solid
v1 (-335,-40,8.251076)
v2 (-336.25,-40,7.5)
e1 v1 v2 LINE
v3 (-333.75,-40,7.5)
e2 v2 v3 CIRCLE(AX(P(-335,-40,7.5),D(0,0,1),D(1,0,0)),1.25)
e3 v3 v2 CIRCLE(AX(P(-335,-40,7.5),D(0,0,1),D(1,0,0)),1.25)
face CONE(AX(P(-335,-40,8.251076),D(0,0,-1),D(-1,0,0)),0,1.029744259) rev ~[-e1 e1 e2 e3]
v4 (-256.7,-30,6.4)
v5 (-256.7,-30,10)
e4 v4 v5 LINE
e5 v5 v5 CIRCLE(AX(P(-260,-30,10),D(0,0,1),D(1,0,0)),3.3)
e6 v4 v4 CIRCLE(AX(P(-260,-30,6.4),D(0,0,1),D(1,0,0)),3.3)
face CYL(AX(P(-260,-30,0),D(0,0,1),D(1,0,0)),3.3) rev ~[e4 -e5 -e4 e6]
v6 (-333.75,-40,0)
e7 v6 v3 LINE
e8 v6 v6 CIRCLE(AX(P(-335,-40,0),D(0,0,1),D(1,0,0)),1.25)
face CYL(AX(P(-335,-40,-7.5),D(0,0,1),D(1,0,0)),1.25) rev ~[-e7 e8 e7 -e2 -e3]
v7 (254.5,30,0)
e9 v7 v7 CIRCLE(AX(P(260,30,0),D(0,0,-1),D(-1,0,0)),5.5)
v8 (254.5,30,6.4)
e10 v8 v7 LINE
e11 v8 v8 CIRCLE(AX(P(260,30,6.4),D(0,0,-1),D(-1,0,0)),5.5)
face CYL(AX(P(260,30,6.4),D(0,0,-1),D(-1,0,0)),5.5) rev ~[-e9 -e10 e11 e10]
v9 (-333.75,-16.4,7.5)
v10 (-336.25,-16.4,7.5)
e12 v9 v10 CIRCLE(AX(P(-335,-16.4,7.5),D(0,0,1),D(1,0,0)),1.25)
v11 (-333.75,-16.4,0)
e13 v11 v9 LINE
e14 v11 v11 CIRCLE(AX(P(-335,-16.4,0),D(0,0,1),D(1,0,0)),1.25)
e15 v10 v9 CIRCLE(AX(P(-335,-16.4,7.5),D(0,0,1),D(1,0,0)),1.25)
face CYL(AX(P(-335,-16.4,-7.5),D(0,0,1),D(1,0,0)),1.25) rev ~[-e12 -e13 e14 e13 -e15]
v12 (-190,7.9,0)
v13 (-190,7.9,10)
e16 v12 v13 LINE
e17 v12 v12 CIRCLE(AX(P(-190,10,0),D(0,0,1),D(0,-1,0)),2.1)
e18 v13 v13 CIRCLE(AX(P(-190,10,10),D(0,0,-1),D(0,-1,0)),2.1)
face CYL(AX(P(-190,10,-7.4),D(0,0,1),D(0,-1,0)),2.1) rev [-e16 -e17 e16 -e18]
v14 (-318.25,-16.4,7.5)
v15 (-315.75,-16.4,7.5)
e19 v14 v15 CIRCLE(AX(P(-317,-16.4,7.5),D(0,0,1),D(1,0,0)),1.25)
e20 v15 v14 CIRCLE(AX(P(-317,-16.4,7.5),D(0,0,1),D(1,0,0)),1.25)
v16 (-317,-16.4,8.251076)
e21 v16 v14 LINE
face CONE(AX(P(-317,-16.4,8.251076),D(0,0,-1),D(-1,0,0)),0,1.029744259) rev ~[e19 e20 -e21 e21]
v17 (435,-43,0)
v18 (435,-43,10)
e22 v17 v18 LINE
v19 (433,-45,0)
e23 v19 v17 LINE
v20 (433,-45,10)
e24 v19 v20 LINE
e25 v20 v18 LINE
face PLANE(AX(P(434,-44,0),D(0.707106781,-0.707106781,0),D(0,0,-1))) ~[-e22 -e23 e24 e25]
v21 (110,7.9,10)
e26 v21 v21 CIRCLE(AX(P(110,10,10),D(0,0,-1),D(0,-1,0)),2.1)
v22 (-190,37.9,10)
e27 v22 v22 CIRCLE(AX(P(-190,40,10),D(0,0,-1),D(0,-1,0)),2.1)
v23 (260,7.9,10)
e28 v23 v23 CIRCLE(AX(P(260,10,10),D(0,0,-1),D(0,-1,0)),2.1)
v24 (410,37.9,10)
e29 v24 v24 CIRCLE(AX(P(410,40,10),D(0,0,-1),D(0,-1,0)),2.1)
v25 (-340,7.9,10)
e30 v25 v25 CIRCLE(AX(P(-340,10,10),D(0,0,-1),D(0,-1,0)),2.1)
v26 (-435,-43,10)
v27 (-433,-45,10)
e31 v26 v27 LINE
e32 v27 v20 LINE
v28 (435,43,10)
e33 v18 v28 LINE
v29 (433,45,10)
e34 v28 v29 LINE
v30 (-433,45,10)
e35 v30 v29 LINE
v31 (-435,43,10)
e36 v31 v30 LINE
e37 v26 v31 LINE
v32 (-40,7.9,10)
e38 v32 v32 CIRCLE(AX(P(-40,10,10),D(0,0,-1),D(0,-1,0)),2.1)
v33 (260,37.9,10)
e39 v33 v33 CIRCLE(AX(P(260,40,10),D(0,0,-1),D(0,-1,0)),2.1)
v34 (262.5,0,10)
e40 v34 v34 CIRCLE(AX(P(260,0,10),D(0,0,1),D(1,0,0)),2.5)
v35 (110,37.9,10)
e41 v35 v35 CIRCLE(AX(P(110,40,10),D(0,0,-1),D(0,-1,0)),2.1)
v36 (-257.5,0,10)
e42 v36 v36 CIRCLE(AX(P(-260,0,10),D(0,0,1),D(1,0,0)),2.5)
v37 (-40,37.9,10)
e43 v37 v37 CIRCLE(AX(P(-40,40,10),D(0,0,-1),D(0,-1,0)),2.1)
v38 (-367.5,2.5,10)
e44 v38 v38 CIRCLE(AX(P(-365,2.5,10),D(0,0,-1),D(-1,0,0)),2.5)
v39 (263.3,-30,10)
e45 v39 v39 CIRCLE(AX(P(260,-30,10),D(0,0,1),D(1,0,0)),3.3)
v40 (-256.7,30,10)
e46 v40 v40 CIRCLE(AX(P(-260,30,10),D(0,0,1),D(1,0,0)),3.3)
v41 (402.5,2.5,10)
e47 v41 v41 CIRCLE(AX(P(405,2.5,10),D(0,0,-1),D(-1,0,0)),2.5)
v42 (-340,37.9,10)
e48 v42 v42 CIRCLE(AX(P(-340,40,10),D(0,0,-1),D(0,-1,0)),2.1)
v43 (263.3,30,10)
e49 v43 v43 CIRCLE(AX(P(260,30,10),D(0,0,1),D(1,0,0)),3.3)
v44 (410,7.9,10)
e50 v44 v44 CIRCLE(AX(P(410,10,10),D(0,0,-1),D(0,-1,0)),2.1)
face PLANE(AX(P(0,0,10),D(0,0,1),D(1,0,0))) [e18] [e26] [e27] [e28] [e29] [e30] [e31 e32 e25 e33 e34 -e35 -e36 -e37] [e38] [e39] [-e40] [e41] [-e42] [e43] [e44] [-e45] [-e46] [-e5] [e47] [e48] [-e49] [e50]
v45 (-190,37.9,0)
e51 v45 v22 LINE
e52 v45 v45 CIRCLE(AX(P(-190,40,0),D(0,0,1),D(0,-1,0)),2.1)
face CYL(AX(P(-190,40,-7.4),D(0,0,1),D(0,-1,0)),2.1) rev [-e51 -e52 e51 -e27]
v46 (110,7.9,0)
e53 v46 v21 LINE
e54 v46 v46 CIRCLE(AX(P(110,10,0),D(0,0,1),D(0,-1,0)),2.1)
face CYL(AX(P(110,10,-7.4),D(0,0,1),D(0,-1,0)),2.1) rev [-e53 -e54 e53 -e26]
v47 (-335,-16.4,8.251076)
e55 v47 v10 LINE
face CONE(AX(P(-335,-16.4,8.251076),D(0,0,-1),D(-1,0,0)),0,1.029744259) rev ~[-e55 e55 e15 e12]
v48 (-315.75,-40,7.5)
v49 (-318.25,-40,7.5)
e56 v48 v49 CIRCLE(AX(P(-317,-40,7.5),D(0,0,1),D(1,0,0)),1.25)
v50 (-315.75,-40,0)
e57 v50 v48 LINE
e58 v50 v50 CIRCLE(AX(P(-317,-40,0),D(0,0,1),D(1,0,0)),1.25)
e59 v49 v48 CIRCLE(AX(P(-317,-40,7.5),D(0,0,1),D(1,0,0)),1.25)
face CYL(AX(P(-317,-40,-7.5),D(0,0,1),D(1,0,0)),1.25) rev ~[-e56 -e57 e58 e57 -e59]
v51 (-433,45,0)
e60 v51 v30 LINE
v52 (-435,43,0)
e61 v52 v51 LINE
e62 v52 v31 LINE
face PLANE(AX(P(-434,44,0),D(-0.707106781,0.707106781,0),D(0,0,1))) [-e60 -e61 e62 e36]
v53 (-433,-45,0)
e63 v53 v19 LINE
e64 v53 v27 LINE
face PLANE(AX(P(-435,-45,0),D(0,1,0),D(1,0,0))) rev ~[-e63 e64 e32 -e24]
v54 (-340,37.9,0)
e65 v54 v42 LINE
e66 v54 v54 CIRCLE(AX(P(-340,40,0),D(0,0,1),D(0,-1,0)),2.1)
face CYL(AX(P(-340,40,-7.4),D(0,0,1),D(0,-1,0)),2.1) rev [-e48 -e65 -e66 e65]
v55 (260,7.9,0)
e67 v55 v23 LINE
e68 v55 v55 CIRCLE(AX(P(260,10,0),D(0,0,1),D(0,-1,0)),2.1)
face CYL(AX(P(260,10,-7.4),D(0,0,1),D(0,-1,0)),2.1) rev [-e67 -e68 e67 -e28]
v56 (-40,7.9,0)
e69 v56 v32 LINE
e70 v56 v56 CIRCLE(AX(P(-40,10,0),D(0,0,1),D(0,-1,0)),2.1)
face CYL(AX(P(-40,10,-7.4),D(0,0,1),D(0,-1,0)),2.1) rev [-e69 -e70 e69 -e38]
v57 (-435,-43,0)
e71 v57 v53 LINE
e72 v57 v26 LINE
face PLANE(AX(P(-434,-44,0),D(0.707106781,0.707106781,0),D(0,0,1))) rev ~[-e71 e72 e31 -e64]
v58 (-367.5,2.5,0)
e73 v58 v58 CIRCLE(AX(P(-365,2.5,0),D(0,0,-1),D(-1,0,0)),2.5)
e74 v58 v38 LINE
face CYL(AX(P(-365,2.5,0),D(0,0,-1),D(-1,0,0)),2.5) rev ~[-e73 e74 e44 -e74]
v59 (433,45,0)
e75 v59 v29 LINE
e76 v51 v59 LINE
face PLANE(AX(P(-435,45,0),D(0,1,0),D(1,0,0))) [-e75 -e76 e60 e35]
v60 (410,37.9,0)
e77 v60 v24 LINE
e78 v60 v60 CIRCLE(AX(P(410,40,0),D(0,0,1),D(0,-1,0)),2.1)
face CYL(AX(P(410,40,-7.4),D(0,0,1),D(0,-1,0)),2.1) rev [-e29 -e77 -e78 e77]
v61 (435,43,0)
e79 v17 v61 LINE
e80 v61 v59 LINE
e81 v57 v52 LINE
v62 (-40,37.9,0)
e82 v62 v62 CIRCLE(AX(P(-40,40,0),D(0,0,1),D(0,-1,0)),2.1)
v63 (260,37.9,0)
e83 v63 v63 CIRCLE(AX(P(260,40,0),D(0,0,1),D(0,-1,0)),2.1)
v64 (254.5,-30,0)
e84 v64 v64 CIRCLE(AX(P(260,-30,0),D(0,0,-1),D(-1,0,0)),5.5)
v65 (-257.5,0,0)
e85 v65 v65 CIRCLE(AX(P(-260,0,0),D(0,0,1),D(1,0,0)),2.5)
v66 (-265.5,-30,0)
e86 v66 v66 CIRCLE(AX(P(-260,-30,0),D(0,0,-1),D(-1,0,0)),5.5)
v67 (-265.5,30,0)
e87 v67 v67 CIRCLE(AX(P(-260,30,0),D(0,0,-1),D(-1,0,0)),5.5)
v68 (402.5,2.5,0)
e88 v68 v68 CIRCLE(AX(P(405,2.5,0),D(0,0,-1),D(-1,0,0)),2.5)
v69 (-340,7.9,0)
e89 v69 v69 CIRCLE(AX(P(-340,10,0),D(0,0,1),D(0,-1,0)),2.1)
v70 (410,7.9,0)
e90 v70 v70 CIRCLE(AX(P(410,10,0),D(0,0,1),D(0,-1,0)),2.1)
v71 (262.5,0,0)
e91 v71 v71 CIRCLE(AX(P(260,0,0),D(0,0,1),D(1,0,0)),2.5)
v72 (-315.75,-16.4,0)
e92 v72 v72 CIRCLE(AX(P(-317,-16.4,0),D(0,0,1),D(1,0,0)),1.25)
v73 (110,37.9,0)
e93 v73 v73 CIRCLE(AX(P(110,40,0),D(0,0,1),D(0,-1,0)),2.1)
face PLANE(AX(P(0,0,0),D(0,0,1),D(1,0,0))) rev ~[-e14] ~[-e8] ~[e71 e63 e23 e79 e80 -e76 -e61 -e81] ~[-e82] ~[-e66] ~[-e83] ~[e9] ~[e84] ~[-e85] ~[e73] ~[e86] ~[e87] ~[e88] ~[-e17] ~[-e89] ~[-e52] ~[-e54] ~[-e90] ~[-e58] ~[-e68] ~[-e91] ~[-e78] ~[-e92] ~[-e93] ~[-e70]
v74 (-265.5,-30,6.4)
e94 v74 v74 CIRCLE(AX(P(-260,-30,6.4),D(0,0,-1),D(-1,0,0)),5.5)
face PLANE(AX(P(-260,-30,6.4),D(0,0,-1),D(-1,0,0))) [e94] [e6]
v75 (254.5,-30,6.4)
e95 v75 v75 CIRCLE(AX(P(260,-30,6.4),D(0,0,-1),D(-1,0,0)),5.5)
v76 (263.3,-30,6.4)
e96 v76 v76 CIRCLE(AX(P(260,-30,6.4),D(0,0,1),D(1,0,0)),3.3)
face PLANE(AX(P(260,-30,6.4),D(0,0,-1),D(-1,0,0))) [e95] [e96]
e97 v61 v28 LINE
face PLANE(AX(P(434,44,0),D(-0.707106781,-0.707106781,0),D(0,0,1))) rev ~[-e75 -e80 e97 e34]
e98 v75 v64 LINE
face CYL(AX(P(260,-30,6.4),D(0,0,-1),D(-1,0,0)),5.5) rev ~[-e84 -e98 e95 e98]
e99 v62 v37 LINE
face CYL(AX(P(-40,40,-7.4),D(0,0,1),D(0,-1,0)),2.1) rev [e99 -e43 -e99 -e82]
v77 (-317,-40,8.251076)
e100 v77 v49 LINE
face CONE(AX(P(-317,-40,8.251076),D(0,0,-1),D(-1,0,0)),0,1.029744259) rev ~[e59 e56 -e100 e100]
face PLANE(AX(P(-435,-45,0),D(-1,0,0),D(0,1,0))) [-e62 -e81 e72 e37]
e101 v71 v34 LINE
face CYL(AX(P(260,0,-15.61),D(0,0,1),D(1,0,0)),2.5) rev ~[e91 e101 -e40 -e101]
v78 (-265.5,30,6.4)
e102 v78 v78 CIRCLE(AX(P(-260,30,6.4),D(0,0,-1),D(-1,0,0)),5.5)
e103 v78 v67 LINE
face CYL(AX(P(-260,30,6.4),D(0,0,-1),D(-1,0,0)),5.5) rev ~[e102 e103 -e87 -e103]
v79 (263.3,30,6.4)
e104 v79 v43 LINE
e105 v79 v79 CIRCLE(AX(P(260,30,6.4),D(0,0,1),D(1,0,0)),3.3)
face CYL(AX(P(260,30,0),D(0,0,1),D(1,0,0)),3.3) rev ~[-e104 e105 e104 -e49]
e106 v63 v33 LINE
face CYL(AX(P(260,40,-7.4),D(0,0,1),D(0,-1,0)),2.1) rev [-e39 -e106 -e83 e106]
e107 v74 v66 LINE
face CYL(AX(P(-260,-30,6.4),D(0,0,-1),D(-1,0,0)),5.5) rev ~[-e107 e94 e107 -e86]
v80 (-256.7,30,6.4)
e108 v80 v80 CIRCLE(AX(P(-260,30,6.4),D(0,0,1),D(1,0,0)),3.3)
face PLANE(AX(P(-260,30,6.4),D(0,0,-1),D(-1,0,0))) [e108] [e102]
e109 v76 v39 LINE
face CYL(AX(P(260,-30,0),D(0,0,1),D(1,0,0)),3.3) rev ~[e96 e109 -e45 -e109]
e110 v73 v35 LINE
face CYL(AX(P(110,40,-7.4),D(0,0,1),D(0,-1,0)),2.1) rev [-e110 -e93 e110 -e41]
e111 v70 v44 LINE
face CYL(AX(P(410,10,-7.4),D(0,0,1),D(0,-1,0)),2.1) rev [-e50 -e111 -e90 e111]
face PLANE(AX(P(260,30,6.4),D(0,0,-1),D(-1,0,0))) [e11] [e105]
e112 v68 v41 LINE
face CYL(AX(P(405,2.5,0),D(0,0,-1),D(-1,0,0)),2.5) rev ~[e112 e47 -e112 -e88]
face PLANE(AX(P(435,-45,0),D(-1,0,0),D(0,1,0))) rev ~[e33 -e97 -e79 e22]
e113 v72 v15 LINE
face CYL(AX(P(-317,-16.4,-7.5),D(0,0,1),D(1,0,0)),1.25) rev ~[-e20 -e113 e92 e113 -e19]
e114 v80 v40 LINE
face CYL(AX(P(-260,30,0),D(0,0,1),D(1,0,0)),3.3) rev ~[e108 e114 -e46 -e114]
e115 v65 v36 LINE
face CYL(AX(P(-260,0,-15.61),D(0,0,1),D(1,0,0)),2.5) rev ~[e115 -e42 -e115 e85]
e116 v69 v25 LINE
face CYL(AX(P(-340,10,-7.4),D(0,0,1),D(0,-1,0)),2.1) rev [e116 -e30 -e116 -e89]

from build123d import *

# Parameters (mm, degrees)
SKETCH_1_W                   = 870
SKETCH_1_H                   = 90
EXTRUDE_1_DEPTH              = 10
CHAMFER_1_SIZE               = 2
HOLE_WIZARD_M6_1_D           = 6.6
HOLE_WIZARD_M6_1_CBORE_D     = 11
HOLE_WIZARD_M6_1_CBORE_DEPTH = 6.4
HOLE_WIZARD_5_0_5_1_D        = 5
HOLE_WIZARD_5_0_5_1_DEPTH    = 15.61
HOLE_WIZARD_5_0_5_1_TIP      = 1.443375673
SKETCH_8_R                   = 2.5
CUT_EXTRUDE_1_DEPTH          = 438.435709562
HOLE_WIZARD_M5_2_AT_2_COUNT  = 2
HOLE_WIZARD_M5_2_AT_2_PITCH  = 30
PATTERN_LINEAR_1_COUNT       = 6
PATTERN_LINEAR_1_PITCH       = 150
HOLE_WIZARD_M3_1_D           = 2.5
HOLE_WIZARD_M3_1_DEPTH       = 7.5
HOLE_WIZARD_M3_1_TIP         = 0.751075774


with BuildPart() as part:
    # 草图1 → 凸台-拉伸1 (new body)
    with BuildSketch(Plane.XY):
        Rectangle(SKETCH_1_W, SKETCH_1_H)
    extrude(amount=EXTRUDE_1_DEPTH)

    # 倒角1
    chamfer_1_edges = [part.edges().sort_by_distance(p)[0] for p in [
        (435, -45, 5),
        (-435, -45, 5),
        (-435, 45, 5),
        (435, 45, 5),
    ]]
    chamfer(chamfer_1_edges, length=CHAMFER_1_SIZE)

    # M6 六角凹头螺钉的柱形沉头孔1 (through all)
    with Locations(Plane(origin=(0, 0, 0), x_dir=(-1, 0, 0), z_dir=(0, 0, -1))):
        with Locations((-260, 30), (-260, -30), (260, -30), (260, 30), (-105.244391783, -69.250649642)):
            CounterBoreHole(HOLE_WIZARD_M6_1_D / 2, HOLE_WIZARD_M6_1_CBORE_D / 2, HOLE_WIZARD_M6_1_CBORE_DEPTH)

    # Ø5.0 (5) 直径孔1
    with Locations(Plane(origin=(0, 0, 0), x_dir=(-1, 0, 0), z_dir=(0, 0, -1))):
        with Locations((-260, 0), (260, 0)):
            Hole(HOLE_WIZARD_5_0_5_1_D / 2, depth=HOLE_WIZARD_5_0_5_1_DEPTH)
            with Locations((0, 0, -(HOLE_WIZARD_5_0_5_1_DEPTH + HOLE_WIZARD_5_0_5_1_TIP / 2))):  # 120° drill point
                Cone(0, HOLE_WIZARD_5_0_5_1_D / 2, HOLE_WIZARD_5_0_5_1_TIP, mode=Mode.SUBTRACT)

    # 草图8 → 切除-拉伸1 (cut, through all)
    with BuildSketch(Plane(origin=(0, 0, 0), x_dir=(-1, 0, 0), z_dir=(0, 0, -1))):
        with Locations((365, 2.5)):
            Circle(SKETCH_8_R)
        with Locations((-405, 2.5)):
            Circle(SKETCH_8_R)
    extrude(amount=-CUT_EXTRUDE_1_DEPTH, mode=Mode.SUBTRACT)

    # 草图9 → M5 螺纹孔2 (revolve, cut)
    with BuildSketch(Plane(origin=(410, 40, 10), x_dir=(0, -1, 0), z_dir=(1, 0, 0))):
        Polygon((0, 0), (0, 18.6618073), (2.1, 17.4), (2.1, 0), align=None)
    hole_wizard_m5_2 = revolve(axis=Axis((410, 40, 16.35), (0, 0, -1)), mode=Mode.SUBTRACT)

    # M5 螺纹孔2 at 2: M5 螺纹孔2 ×2
    with Locations(*[(0, -i * HOLE_WIZARD_M5_2_AT_2_PITCH, 0) for i in range(1, HOLE_WIZARD_M5_2_AT_2_COUNT)]):
        add(hole_wizard_m5_2, mode=Mode.SUBTRACT)

    # 阵列(线性)1: M5 螺纹孔2 ×6
    with Locations(*[(-i * PATTERN_LINEAR_1_PITCH, 0, 0) for i in range(1, PATTERN_LINEAR_1_COUNT)]):
        add(hole_wizard_m5_2, mode=Mode.SUBTRACT)

    # 阵列(线性)1 copy 1 sketch → 阵列(线性)1 copy 1 (revolve, cut)
    with BuildSketch(Plane(origin=(260, 10, 10), x_dir=(0, -1, 0), z_dir=(1, 0, 0))):
        Polygon((0, 0), (0, 18.6618073), (2.1, 17.4), (2.1, 0), align=None)
    revolve(axis=Axis((260, 10, 16.35), (0, 0, -1)), mode=Mode.SUBTRACT)

    # 阵列(线性)1 copy 2 sketch → 阵列(线性)1 copy 2 (revolve, cut)
    with BuildSketch(Plane(origin=(110, 10, 10), x_dir=(0, -1, 0), z_dir=(1, 0, 0))):
        Polygon((0, 0), (0, 18.6618073), (2.1, 17.4), (2.1, 0), align=None)
    revolve(axis=Axis((110, 10, 16.35), (0, 0, -1)), mode=Mode.SUBTRACT)

    # 阵列(线性)1 copy 3 sketch → 阵列(线性)1 copy 3 (revolve, cut)
    with BuildSketch(Plane(origin=(-40, 10, 10), x_dir=(0, -1, 0), z_dir=(1, 0, 0))):
        Polygon((0, 0), (0, 18.6618073), (2.1, 17.4), (2.1, 0), align=None)
    revolve(axis=Axis((-40, 10, 16.35), (0, 0, -1)), mode=Mode.SUBTRACT)

    # 阵列(线性)1 copy 4 sketch → 阵列(线性)1 copy 4 (revolve, cut)
    with BuildSketch(Plane(origin=(-190, 10, 10), x_dir=(0, -1, 0), z_dir=(1, 0, 0))):
        Polygon((0, 0), (0, 18.6618073), (2.1, 17.4), (2.1, 0), align=None)
    revolve(axis=Axis((-190, 10, 16.35), (0, 0, -1)), mode=Mode.SUBTRACT)

    # 阵列(线性)1 copy 5 sketch → 阵列(线性)1 copy 5 (revolve, cut)
    with BuildSketch(Plane(origin=(-340, 10, 10), x_dir=(0, -1, 0), z_dir=(1, 0, 0))):
        Polygon((0, 0), (0, 18.6618073), (2.1, 17.4), (2.1, 0), align=None)
    revolve(axis=Axis((-340, 10, 16.35), (0, 0, -1)), mode=Mode.SUBTRACT)

    # M3 螺纹孔1
    with Locations(Plane(origin=(0, 0, 0), x_dir=(-1, 0, 0), z_dir=(0, 0, -1))):
        with Locations((317, -16.4), (317, -40), (335, -40), (335, -16.4)):
            Hole(HOLE_WIZARD_M3_1_D / 2, depth=HOLE_WIZARD_M3_1_DEPTH)
            with Locations((0, 0, -(HOLE_WIZARD_M3_1_DEPTH + HOLE_WIZARD_M3_1_TIP / 2))):  # 118° drill point
                Cone(0, HOLE_WIZARD_M3_1_D / 2, HOLE_WIZARD_M3_1_TIP, mode=Mode.SUBTRACT)


solid = part.part
